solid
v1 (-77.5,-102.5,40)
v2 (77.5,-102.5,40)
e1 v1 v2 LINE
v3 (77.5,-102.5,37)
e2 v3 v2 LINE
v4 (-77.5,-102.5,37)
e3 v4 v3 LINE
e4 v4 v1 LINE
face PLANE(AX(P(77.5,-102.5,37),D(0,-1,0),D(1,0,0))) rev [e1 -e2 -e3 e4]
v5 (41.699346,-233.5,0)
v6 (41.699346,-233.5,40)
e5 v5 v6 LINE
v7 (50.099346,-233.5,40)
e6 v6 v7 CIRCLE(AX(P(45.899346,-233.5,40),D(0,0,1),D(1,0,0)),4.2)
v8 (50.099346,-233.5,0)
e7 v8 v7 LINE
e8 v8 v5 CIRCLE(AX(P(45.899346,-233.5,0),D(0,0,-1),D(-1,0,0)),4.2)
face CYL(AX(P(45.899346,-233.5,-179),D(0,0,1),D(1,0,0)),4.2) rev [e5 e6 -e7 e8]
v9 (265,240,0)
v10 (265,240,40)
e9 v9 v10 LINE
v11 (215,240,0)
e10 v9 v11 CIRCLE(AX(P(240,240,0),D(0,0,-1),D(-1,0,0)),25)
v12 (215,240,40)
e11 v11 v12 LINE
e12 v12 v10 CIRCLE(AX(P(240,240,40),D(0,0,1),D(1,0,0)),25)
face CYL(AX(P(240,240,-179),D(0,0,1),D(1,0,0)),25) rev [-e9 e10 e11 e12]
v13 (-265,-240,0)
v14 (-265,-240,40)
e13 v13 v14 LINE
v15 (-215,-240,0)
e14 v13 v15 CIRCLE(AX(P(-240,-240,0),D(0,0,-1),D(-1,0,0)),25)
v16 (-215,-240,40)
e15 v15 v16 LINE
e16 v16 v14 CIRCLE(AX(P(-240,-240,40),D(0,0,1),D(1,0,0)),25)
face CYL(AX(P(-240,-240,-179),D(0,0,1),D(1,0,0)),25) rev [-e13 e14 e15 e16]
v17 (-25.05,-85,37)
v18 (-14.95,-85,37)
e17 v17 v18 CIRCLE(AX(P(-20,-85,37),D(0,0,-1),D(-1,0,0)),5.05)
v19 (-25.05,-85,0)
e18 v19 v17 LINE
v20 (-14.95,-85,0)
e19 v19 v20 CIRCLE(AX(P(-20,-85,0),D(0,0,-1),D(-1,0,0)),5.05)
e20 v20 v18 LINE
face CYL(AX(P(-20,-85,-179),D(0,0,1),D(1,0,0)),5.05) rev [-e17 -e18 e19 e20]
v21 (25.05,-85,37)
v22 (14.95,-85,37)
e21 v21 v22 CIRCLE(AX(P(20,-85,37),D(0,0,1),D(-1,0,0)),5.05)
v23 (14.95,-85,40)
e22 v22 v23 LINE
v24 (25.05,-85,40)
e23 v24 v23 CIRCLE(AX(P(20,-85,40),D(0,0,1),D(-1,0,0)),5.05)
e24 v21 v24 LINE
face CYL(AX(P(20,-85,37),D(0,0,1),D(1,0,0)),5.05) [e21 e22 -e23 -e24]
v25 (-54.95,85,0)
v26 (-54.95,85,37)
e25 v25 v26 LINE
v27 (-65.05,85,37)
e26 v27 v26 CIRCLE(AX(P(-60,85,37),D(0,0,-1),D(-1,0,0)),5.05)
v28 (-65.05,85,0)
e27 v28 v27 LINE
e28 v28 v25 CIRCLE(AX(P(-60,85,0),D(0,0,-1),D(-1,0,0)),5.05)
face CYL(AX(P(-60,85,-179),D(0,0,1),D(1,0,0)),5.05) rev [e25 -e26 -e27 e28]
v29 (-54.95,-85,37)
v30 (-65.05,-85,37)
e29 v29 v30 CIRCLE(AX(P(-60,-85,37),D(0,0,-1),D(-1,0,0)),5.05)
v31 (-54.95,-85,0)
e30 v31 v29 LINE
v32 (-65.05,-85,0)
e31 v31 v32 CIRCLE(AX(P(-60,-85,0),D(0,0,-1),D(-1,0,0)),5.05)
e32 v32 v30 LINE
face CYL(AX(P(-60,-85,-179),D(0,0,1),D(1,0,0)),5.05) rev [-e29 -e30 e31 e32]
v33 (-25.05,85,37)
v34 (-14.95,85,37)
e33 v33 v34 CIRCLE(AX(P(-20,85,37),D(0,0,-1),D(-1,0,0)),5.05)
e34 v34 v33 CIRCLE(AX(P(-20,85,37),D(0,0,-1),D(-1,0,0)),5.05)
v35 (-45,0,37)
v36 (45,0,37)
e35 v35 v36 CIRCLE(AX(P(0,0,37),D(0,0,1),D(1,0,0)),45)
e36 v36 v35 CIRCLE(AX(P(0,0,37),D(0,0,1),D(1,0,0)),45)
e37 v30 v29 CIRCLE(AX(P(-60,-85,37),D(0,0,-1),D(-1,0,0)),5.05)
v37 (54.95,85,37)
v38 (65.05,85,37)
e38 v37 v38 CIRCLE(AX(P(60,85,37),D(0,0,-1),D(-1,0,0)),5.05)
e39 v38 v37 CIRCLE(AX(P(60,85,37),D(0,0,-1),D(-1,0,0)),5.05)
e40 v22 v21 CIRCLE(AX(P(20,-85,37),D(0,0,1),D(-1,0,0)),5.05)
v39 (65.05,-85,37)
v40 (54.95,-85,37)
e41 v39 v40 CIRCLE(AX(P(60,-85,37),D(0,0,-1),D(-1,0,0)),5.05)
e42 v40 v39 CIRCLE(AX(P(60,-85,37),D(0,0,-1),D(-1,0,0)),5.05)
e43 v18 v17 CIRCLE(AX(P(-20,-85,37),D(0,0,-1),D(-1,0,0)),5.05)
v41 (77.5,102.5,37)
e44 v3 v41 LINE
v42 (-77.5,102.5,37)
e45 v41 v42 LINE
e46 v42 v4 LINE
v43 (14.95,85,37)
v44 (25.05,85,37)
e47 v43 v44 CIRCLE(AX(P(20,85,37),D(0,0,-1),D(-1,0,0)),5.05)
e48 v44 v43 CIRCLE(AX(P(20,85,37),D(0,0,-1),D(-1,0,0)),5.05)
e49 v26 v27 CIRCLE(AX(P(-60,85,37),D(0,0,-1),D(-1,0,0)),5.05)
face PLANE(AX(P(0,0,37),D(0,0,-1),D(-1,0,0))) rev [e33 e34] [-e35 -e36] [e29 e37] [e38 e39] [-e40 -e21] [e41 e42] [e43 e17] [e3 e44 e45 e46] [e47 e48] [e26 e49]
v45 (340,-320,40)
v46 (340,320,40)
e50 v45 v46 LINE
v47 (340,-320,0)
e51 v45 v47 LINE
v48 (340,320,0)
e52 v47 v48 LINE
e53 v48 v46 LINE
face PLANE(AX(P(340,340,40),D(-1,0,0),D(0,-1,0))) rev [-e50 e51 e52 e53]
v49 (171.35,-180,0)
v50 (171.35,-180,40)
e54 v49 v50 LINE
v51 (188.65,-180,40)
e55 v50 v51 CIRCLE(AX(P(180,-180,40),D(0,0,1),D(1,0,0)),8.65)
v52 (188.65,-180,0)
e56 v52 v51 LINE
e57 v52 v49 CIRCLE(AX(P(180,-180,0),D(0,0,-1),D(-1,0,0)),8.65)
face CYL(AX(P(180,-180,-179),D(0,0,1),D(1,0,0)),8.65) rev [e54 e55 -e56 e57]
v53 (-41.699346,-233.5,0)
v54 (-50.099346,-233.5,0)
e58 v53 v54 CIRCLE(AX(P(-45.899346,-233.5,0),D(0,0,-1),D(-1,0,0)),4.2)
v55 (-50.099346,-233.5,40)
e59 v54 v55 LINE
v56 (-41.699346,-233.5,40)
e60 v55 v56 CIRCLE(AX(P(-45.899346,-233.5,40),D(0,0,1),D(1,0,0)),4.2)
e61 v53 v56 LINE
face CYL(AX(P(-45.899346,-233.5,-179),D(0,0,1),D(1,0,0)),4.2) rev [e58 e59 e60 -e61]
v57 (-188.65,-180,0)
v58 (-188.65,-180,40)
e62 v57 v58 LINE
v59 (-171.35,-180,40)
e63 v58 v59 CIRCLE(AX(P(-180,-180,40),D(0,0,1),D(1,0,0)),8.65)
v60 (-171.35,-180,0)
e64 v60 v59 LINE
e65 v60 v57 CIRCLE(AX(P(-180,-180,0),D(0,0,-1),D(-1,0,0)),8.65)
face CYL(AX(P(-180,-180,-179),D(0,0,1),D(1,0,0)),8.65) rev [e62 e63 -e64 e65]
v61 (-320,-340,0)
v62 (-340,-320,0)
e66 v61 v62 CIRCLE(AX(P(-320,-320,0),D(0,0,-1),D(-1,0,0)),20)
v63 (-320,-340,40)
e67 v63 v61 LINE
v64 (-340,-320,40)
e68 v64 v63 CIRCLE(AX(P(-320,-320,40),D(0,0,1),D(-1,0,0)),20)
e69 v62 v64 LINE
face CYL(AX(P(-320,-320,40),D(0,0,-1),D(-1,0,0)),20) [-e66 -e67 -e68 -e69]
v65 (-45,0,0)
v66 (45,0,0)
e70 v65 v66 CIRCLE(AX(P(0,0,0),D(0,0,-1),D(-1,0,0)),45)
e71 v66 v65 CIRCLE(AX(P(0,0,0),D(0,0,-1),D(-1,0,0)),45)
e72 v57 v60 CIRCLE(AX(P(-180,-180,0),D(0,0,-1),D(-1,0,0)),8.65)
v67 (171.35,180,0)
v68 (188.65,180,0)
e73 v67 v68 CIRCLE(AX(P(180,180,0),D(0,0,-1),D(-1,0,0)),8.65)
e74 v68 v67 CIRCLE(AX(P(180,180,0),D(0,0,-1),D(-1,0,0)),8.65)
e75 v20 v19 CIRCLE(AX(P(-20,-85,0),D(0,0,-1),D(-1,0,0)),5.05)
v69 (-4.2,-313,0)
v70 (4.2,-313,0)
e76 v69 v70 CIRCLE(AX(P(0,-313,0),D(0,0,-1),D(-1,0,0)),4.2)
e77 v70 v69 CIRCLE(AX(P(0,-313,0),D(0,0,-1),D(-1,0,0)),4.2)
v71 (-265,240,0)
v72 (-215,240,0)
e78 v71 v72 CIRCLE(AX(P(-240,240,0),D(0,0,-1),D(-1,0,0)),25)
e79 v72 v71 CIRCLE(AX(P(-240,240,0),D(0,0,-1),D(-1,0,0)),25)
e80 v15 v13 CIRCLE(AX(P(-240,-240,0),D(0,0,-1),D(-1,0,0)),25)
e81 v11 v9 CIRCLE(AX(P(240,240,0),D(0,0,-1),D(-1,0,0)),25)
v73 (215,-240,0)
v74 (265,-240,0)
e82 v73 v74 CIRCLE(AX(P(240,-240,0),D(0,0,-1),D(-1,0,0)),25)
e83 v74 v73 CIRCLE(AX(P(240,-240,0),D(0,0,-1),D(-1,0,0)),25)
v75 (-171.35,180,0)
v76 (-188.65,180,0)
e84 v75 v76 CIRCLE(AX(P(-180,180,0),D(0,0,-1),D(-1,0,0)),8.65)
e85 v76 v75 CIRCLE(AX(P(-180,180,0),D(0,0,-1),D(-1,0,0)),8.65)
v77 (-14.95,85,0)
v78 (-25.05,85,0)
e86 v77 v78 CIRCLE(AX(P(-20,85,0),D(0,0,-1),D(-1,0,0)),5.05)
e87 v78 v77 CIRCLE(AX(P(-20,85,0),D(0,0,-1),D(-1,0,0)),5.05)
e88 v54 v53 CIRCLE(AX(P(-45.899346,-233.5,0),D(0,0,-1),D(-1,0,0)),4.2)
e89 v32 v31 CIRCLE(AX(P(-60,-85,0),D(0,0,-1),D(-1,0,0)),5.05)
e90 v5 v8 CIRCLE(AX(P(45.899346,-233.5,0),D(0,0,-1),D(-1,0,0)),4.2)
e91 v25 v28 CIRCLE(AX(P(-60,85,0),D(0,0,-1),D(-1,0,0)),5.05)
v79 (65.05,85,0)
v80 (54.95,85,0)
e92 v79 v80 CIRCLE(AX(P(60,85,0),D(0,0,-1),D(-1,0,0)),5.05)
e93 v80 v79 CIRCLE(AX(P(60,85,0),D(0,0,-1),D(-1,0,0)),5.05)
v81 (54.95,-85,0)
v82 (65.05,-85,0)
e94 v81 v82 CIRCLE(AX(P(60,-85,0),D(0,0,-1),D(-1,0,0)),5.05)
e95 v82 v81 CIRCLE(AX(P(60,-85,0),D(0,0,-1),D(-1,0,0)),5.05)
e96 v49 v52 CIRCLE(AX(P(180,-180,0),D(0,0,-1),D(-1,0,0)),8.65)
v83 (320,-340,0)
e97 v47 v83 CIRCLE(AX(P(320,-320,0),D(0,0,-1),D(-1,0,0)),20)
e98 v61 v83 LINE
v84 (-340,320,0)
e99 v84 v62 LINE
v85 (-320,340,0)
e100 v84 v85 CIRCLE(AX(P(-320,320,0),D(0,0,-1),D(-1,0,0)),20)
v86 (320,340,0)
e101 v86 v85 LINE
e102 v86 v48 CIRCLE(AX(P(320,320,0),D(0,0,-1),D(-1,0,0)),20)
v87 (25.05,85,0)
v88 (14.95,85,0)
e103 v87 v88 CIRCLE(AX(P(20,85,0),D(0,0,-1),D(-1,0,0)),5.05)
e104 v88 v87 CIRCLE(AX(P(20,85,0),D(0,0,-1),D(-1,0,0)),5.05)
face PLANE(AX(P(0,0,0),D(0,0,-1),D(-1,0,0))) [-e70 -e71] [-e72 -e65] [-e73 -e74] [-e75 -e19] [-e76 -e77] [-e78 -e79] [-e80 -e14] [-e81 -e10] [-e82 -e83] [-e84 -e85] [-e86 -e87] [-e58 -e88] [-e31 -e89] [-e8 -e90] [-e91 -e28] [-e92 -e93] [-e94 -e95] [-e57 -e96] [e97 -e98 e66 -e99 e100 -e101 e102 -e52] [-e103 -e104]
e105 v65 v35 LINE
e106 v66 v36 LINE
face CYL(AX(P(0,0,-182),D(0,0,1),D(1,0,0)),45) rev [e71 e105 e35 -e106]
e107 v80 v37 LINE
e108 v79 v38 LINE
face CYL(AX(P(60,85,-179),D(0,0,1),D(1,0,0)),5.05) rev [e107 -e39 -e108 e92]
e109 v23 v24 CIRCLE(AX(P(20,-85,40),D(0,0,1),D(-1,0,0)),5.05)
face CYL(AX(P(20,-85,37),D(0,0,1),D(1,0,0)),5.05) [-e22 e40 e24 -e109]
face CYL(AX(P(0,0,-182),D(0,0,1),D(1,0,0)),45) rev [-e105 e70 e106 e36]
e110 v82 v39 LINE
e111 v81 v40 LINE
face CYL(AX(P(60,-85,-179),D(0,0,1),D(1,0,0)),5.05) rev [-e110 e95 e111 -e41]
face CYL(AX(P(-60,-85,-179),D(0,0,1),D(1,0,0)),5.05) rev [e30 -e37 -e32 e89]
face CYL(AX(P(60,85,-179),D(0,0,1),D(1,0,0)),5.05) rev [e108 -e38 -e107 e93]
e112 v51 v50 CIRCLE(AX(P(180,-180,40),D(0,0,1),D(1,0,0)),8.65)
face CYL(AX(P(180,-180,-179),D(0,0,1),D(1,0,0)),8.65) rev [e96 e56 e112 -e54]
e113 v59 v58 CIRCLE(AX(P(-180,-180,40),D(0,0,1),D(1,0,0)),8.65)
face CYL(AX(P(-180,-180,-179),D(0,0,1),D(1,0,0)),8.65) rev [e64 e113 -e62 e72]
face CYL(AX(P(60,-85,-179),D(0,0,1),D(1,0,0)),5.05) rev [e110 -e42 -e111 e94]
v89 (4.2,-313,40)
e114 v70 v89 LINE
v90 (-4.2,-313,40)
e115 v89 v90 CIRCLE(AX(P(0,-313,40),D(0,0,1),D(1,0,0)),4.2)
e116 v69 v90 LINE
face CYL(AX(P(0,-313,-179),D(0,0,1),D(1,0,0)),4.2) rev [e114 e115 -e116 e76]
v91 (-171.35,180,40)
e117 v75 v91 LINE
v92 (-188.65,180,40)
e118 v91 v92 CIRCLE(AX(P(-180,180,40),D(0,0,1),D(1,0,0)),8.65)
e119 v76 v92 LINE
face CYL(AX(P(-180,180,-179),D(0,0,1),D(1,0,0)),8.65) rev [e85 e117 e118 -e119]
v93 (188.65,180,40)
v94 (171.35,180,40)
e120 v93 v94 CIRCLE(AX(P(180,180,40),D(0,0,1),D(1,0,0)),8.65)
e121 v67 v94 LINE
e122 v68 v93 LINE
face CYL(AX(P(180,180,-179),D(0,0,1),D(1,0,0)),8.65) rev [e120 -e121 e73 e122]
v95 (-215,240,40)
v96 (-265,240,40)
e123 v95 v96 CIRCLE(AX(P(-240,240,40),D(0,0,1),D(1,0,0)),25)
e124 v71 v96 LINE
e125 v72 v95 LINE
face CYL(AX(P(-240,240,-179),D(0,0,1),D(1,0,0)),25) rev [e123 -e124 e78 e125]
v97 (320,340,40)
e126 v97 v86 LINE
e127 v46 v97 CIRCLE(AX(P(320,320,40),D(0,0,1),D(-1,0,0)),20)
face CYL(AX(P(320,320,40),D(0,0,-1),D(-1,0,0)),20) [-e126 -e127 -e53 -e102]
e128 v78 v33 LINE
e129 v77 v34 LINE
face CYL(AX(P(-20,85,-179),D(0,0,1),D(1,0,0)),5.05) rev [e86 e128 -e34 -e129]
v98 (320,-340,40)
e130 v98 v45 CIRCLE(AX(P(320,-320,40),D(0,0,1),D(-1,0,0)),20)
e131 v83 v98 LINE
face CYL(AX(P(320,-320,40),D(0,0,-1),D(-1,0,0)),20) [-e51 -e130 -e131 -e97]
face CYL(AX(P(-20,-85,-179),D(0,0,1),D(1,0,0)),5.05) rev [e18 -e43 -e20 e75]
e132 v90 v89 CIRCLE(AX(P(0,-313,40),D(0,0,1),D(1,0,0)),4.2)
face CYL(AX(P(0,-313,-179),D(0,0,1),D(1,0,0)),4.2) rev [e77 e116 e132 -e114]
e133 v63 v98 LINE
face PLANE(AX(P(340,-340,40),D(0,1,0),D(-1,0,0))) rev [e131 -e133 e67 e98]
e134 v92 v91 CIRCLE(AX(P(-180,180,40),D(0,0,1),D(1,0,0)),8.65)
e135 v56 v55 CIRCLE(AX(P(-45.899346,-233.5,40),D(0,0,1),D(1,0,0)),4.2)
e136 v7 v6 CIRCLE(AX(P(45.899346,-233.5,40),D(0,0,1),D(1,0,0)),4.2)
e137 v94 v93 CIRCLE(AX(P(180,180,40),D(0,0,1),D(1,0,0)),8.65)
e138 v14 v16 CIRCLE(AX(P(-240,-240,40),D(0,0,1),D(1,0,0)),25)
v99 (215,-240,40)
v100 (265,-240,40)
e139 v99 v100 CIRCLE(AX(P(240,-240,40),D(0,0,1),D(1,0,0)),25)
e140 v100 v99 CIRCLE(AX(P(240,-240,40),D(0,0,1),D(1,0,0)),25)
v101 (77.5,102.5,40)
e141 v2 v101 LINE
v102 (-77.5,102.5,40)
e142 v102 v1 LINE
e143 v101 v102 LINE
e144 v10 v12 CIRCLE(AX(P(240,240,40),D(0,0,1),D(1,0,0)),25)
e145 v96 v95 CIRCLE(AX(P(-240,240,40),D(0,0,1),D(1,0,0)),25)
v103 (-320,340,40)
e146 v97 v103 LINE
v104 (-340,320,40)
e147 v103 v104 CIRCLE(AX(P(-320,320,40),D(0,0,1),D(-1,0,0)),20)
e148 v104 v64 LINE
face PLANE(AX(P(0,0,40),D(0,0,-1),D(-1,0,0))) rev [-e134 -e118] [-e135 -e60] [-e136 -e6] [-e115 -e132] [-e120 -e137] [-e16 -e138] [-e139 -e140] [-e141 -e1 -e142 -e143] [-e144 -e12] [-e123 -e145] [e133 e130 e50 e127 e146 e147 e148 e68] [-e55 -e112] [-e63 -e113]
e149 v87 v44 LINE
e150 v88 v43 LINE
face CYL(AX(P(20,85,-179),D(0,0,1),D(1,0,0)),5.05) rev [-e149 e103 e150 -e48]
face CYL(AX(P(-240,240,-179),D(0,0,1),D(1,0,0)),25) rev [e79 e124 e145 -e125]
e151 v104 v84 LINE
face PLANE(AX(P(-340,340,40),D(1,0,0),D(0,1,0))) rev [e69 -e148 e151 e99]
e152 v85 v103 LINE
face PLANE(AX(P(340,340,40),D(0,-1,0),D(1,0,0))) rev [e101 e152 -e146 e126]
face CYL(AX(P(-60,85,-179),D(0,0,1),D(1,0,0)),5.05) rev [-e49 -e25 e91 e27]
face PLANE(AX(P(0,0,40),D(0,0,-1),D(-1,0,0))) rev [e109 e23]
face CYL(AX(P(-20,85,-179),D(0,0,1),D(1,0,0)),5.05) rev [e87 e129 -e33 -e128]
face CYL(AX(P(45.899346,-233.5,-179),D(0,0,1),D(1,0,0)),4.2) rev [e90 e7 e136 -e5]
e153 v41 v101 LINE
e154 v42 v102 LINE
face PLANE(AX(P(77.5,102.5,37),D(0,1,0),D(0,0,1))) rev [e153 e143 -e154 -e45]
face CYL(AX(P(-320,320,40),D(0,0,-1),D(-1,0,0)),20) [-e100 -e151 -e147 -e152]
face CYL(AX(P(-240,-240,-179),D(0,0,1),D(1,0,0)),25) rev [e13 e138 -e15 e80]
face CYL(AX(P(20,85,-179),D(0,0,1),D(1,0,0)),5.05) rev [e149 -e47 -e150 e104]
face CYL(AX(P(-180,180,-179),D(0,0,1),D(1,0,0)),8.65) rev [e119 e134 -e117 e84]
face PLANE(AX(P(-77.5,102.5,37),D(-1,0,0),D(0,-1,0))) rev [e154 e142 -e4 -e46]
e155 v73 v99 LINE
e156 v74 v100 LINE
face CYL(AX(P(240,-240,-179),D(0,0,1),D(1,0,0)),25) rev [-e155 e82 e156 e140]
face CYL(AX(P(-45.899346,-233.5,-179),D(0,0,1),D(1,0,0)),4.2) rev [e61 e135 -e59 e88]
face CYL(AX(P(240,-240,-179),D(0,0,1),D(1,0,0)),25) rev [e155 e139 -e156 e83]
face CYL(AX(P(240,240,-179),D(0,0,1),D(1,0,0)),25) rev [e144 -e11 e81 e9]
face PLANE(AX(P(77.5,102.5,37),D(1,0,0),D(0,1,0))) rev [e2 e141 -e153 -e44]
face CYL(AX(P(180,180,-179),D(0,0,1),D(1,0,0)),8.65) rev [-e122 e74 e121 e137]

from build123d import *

# Parameters (mm, degrees)
SKETCH1_W           = 680
SKETCH1_H           = 680
BOSS_EXTRUDE1_DEPTH = 40
FILLET1_R           = 20
SKETCH2_W           = 155
SKETCH2_H           = 205
SKETCH2_R           = 5.05
CUT_EXTRUDE1_DEPTH  = 3
SKETCH3_R           = 5.05
CUT_EXTRUDE2_DEPTH  = 219
SKETCH4_R           = 45
CUT_EXTRUDE3_DEPTH  = 219
SKETCH5_R           = 8.65
CUT_EXTRUDE4_DEPTH  = 219
SKETCH6_R           = 4.2
CUT_EXTRUDE5_DEPTH  = 219
SKETCH7_R           = 25
CUT_EXTRUDE6_DEPTH  = 219


with BuildPart() as part:
    # Sketch1 → Boss-Extrude1 (new body)
    with BuildSketch(Plane.XY):
        Rectangle(SKETCH1_W, SKETCH1_H)
    extrude(amount=BOSS_EXTRUDE1_DEPTH)

    # Fillet1
    fillet1_edges = [part.edges().sort_by_distance(p)[0] for p in [
        (-340, 340, 20),
        (340, 340, 20),
        (340, -340, 20),
        (-340, -340, 20),
    ]]
    fillet(fillet1_edges, radius=FILLET1_R)

    # Sketch2 → Cut-Extrude1 (cut)
    with BuildSketch(Plane.XY.offset(40)):
        Rectangle(SKETCH2_W, SKETCH2_H)
        with Locations((-60, 85)):
            Circle(SKETCH2_R, mode=Mode.SUBTRACT)
        with Locations((-20, 85)):
            Circle(SKETCH2_R, mode=Mode.SUBTRACT)
        with Locations((20, 85)):
            Circle(SKETCH2_R, mode=Mode.SUBTRACT)
        with Locations((60, 85)):
            Circle(SKETCH2_R, mode=Mode.SUBTRACT)
        with Locations(Location((60, -85, 0), (0, 0, 180))):
            Circle(SKETCH2_R, mode=Mode.SUBTRACT)
        with Locations(Location((20, -85, 0), (0, 0, 180))):
            Circle(SKETCH2_R, mode=Mode.SUBTRACT)
        with Locations(Location((-20, -85, 0), (0, 0, 180))):
            Circle(SKETCH2_R, mode=Mode.SUBTRACT)
        with Locations(Location((-60, -85, 0), (0, 0, 180))):
            Circle(SKETCH2_R, mode=Mode.SUBTRACT)
    extrude(amount=-CUT_EXTRUDE1_DEPTH, mode=Mode.SUBTRACT)

    # Sketch3 → Cut-Extrude2 (cut)
    with BuildSketch(Plane.XY.offset(40)):
        with Locations(Location((-60, 85, 0), (0, 0, 180))):
            Circle(SKETCH3_R)
        with Locations(Location((-60, -85, 0), (0, 0, 180))):
            Circle(SKETCH3_R)
        with Locations(Location((-20, -85, 0), (0, 0, 180))):
            Circle(SKETCH3_R)
        with Locations(Location((60, -85, 0), (0, 0, 180))):
            Circle(SKETCH3_R)
        with Locations(Location((60, 85, 0), (0, 0, 180))):
            Circle(SKETCH3_R)
        with Locations(Location((20, 85, 0), (0, 0, 180))):
            Circle(SKETCH3_R)
        with Locations(Location((-20, 85, 0), (0, 0, 180))):
            Circle(SKETCH3_R)
    extrude(amount=-CUT_EXTRUDE2_DEPTH, mode=Mode.SUBTRACT)

    # Sketch4 → Cut-Extrude3 (cut)
    with BuildSketch(Plane.XY.offset(37)):
        Circle(SKETCH4_R)
    extrude(amount=-CUT_EXTRUDE3_DEPTH, mode=Mode.SUBTRACT)

    # Sketch5 → Cut-Extrude4 (cut)
    with BuildSketch(Plane.XY.offset(40)):
        with Locations((-180, 180)):
            Circle(SKETCH5_R)
        with Locations((180, 180)):
            Circle(SKETCH5_R)
        with Locations((180, -180)):
            Circle(SKETCH5_R)
        with Locations((-180, -180)):
            Circle(SKETCH5_R)
    extrude(amount=-CUT_EXTRUDE4_DEPTH, mode=Mode.SUBTRACT)

    # Sketch6 → Cut-Extrude5 (cut)
    with BuildSketch(Plane.XY.offset(40)):
        with Locations((0, -313)):
            Circle(SKETCH6_R)
        with Locations((45.899346401, -233.5)):
            Circle(SKETCH6_R)
        with Locations((-45.899346401, -233.5)):
            Circle(SKETCH6_R)
    extrude(amount=-CUT_EXTRUDE5_DEPTH, mode=Mode.SUBTRACT)

    # Sketch7 → Cut-Extrude6 (cut)
    with BuildSketch(Plane.XY.offset(40)):
        with Locations((-240, 240)):
            Circle(SKETCH7_R)
        with Locations((240, 240)):
            Circle(SKETCH7_R)
        with Locations((240, -240)):
            Circle(SKETCH7_R)
        with Locations((-240, -240)):
            Circle(SKETCH7_R)
    extrude(amount=-CUT_EXTRUDE6_DEPTH, mode=Mode.SUBTRACT)


solid = part.part
